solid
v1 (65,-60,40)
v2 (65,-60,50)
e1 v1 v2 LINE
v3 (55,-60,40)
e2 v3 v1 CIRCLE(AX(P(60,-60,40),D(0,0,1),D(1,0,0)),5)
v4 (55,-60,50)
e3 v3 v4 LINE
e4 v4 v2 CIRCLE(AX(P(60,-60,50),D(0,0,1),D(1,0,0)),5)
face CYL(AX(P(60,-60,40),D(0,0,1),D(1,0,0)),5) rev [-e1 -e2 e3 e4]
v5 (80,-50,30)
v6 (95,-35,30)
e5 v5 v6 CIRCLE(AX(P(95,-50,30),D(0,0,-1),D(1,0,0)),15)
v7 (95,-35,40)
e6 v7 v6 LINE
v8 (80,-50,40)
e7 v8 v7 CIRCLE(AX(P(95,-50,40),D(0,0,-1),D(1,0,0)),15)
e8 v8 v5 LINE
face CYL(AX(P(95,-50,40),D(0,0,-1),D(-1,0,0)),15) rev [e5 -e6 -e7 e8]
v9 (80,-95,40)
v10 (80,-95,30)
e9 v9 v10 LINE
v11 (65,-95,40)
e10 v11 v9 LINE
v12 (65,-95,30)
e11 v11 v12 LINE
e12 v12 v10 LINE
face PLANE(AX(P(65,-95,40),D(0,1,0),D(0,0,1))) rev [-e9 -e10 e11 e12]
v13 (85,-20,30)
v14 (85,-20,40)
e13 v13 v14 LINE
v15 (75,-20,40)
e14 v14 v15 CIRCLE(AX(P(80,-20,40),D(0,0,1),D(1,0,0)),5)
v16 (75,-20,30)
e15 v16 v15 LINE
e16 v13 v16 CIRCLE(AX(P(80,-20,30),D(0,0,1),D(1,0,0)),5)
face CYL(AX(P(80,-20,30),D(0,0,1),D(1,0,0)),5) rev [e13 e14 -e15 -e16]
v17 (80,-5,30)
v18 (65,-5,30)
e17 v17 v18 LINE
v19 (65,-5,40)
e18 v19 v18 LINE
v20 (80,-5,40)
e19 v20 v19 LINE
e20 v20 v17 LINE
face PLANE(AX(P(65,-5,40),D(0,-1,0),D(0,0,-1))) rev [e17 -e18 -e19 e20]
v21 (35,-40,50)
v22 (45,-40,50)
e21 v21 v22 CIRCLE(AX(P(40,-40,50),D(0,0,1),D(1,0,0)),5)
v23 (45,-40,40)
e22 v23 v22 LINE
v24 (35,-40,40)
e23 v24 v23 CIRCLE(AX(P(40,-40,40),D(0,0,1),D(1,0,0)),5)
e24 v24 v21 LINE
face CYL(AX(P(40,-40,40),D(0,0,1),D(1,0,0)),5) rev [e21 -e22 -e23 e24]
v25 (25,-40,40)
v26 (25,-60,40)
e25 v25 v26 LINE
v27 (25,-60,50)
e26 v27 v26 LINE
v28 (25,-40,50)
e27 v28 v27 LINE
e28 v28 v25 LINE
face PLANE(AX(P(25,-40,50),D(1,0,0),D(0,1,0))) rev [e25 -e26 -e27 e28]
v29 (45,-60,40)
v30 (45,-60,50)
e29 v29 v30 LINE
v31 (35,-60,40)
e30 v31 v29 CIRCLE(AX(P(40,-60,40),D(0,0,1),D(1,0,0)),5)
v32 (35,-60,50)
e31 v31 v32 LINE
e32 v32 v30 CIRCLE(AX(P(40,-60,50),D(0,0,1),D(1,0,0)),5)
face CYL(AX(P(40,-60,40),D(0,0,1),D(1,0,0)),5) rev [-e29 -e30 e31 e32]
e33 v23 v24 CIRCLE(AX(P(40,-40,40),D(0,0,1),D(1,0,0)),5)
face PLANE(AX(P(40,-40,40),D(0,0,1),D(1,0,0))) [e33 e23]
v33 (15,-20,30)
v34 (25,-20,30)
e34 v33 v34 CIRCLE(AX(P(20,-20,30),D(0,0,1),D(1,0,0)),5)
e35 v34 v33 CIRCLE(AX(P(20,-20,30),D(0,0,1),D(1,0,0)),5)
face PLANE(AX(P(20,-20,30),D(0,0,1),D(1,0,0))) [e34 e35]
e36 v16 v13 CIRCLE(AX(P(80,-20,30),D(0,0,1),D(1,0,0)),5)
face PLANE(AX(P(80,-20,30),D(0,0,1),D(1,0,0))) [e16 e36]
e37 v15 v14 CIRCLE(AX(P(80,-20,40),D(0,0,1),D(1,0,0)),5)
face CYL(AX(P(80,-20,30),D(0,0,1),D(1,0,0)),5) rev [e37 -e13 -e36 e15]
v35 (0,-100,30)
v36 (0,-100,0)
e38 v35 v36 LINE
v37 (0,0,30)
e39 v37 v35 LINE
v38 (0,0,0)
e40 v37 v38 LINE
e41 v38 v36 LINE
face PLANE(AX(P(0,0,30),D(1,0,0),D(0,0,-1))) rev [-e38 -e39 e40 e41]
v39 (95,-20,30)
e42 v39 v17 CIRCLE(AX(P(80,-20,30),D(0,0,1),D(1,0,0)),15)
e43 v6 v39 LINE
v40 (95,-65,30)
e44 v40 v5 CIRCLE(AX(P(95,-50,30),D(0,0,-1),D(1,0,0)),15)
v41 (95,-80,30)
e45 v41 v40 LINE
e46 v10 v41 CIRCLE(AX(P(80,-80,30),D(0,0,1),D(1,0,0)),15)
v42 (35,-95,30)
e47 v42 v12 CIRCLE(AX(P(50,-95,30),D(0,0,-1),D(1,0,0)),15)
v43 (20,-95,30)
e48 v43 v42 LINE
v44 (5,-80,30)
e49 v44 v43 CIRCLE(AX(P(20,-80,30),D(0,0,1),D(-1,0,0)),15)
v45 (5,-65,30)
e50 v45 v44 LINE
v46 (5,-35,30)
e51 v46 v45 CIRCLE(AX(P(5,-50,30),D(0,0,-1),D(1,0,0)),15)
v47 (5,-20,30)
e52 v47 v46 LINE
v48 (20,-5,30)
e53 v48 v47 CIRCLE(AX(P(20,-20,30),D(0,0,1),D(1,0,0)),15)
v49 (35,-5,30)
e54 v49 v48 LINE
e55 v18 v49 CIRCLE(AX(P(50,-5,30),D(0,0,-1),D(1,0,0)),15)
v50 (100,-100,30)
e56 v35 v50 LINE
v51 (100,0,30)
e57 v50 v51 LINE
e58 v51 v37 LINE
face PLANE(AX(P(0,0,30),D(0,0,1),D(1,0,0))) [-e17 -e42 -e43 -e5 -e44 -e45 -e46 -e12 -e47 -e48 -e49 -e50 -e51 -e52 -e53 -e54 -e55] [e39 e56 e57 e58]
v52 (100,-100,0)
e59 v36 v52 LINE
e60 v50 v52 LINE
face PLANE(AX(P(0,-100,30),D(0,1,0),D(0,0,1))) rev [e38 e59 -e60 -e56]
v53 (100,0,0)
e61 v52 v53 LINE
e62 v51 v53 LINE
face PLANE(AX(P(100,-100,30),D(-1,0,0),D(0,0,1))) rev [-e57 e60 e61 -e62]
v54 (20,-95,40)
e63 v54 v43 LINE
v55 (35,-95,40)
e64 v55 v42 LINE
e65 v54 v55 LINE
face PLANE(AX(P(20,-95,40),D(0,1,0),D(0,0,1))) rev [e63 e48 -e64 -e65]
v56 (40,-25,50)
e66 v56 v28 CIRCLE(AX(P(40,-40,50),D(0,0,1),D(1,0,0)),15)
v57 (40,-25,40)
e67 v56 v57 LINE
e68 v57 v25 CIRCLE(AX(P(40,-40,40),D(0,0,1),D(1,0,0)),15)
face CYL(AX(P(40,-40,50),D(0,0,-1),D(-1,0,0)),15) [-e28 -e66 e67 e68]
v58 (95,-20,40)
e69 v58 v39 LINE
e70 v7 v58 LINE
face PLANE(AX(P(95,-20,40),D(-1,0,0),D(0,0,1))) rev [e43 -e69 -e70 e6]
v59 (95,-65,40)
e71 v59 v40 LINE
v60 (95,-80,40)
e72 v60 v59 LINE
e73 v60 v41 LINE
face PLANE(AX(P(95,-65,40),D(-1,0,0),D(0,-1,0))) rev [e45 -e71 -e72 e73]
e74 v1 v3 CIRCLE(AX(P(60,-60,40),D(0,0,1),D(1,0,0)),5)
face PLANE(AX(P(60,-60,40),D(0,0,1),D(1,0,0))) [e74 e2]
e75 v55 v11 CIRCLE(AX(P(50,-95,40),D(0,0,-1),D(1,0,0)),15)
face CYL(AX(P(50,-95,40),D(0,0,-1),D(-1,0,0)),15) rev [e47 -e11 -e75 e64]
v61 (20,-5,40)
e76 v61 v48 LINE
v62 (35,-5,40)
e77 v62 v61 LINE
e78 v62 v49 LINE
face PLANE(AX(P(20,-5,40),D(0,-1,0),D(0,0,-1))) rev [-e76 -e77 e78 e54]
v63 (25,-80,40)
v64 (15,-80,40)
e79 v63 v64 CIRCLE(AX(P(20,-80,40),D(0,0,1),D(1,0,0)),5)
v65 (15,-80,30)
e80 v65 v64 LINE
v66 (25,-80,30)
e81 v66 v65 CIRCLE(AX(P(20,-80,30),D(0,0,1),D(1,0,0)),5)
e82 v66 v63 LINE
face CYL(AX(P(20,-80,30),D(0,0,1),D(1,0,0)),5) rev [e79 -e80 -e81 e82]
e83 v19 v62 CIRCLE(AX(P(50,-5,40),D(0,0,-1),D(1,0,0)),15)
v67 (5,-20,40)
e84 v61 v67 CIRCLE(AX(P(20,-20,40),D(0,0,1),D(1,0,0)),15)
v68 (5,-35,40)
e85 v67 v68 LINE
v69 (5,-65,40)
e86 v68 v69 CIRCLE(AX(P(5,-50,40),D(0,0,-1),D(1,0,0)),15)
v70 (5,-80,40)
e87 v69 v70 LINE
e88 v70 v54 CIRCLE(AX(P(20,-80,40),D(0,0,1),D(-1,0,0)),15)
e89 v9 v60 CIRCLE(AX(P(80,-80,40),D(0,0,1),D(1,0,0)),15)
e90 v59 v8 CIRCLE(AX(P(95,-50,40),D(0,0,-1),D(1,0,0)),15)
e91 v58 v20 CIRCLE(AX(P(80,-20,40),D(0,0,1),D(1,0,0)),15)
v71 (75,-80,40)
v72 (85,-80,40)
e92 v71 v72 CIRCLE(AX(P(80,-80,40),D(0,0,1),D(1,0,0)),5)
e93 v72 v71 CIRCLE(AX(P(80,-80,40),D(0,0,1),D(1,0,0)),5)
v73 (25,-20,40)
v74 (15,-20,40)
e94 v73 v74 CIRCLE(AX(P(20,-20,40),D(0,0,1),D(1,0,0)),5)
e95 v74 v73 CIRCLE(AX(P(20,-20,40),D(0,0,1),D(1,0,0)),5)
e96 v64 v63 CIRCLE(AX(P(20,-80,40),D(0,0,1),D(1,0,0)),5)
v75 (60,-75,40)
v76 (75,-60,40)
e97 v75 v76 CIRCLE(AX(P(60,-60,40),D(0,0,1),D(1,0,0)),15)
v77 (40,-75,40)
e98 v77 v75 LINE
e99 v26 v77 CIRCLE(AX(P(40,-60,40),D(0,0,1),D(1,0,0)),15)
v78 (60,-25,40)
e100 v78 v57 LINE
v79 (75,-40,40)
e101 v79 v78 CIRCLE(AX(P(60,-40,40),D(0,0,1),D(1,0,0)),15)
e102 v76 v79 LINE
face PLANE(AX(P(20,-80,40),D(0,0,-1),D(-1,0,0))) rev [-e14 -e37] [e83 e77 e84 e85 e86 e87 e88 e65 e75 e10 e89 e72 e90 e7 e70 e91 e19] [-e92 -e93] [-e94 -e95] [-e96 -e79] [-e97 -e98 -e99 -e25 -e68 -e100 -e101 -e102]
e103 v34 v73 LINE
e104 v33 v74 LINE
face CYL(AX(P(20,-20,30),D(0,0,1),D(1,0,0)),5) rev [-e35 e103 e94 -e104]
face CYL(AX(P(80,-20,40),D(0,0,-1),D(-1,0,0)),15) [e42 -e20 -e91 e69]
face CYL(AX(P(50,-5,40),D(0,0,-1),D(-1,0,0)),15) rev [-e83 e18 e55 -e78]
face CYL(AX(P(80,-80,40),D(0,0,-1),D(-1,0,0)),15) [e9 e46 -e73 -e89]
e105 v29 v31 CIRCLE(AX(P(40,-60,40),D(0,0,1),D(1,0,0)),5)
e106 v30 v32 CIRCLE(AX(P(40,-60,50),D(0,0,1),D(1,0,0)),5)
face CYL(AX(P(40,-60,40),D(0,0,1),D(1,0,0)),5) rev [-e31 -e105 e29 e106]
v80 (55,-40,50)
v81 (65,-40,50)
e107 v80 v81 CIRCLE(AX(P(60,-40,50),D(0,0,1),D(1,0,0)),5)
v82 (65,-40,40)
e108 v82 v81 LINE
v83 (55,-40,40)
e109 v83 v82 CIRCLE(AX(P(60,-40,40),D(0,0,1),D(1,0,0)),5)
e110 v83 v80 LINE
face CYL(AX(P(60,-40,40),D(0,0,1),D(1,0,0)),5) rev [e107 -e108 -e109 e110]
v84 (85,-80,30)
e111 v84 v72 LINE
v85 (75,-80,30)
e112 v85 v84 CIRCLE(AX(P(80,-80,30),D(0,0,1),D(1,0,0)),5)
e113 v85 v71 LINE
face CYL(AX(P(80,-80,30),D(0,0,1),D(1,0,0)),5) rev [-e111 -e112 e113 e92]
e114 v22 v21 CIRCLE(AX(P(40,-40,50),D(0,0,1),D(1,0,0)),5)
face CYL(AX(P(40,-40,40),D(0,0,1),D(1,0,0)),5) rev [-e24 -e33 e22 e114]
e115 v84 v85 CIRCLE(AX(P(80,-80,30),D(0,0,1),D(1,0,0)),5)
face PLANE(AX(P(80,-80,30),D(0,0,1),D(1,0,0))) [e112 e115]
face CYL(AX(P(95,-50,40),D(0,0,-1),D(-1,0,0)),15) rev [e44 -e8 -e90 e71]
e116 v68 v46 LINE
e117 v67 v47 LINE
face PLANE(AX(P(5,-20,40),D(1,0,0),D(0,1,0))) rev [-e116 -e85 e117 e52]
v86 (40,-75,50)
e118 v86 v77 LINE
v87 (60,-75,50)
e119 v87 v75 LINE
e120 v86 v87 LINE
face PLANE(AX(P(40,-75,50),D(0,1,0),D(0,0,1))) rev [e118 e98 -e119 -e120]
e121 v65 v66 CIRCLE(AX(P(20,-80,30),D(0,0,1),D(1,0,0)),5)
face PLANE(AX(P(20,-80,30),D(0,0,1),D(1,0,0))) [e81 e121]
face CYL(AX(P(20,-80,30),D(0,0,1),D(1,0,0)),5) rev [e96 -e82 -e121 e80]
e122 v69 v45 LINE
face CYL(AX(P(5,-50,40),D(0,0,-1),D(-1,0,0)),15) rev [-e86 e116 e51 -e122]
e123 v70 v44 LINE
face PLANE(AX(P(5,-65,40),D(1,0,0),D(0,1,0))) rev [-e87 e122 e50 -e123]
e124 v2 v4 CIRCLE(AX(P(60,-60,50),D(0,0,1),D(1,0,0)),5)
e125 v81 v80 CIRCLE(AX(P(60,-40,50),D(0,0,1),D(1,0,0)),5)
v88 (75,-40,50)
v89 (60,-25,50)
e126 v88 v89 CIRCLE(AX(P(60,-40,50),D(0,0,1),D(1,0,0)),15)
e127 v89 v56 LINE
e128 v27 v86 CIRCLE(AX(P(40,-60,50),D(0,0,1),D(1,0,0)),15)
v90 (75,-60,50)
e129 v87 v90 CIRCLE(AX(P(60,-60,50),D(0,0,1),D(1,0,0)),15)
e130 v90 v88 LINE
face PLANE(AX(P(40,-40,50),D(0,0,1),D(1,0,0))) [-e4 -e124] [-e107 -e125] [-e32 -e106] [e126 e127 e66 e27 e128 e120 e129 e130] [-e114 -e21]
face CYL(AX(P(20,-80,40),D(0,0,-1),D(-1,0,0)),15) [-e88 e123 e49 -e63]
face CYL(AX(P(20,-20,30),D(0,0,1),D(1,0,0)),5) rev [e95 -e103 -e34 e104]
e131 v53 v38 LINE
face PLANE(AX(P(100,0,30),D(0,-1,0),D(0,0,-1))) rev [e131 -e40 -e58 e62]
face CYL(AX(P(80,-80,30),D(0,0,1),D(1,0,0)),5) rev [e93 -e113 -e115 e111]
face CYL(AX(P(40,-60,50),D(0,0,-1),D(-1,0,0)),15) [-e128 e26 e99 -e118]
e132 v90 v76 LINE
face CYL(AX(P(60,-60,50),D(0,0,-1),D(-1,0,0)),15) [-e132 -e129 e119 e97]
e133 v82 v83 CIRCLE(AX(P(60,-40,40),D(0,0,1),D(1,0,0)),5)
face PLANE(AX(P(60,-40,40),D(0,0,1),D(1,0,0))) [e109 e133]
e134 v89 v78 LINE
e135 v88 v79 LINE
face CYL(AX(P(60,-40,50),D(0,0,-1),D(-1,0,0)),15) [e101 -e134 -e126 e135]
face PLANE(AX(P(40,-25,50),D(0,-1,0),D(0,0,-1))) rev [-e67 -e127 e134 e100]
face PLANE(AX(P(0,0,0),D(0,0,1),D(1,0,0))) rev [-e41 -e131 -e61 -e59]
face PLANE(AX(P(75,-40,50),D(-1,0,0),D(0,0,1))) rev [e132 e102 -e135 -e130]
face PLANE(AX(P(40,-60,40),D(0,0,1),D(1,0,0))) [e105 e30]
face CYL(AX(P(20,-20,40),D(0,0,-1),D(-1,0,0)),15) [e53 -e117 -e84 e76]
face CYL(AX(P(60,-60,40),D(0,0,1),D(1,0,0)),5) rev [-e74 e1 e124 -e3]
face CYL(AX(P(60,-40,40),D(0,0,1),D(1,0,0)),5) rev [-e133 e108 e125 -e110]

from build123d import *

# Parameters (mm, degrees)
BASE_BLOCK_SKETCH_W         = 100
BASE_BLOCK_SKETCH_H         = 100
BASE_BLOCK_100X100X30_DEPTH = 30
FLANGE_PLATE_DEPTH          = 10
CENTRE_BOSS_DEPTH           = 10
BOSS_HOLES_SKETCH_R         = 5
BOSS_HOLES_4X_10_DEPTH      = 10
FLANGE_HOLES_SKETCH_R       = 5
FLANGE_HOLES_4X_10_DEPTH    = 10


with BuildPart() as part:
    # Base Block Sketch → Base Block 100x100x30 (new body)
    with BuildSketch(Plane.XY):
        with Locations((50, -50)):
            Rectangle(BASE_BLOCK_SKETCH_W, BASE_BLOCK_SKETCH_H)
    extrude(amount=BASE_BLOCK_100X100X30_DEPTH)

    # Flange Plate Sketch → Flange Plate (add)
    with BuildSketch(Plane.XY.offset(30)):
        with BuildLine():
            Line((5, -65), (5, -80))
            ThreePointArc((5, -80), (9.393398282, -90.606601718), (20, -95))
            Line((20, -95), (35, -95))
            ThreePointArc((35, -95), (50, -80), (65, -95))
            Line((65, -95), (80, -95))
            ThreePointArc((80, -95), (90.606601718, -90.606601718), (95, -80))
            Line((95, -80), (95, -65))
            ThreePointArc((95, -65), (80, -50), (95, -35))
            Line((95, -35), (95, -20))
            ThreePointArc((95, -20), (90.606601718, -9.393398282), (80, -5))
            Line((80, -5), (65, -5))
            ThreePointArc((65, -5), (50, -20), (35, -5))
            Line((35, -5), (20, -5))
            ThreePointArc((20, -5), (9.393398282, -9.393398282), (5, -20))
            Line((5, -20), (5, -35))
            ThreePointArc((5, -35), (20, -50), (5, -65))
        make_face()
    extrude(amount=FLANGE_PLATE_DEPTH)

    # Centre Boss Sketch → Centre Boss (add)
    with BuildSketch(Plane.XY.offset(40)):
        with BuildLine():
            Line((25, -40), (25, -60))
            ThreePointArc((25, -60), (29.393398282, -70.606601718), (40, -75))
            Line((40, -75), (60, -75))
            ThreePointArc((60, -75), (70.606601718, -70.606601718), (75, -60))
            Line((75, -60), (75, -40))
            ThreePointArc((75, -40), (70.606601718, -29.393398282), (60, -25))
            Line((60, -25), (40, -25))
            ThreePointArc((40, -25), (29.393398282, -29.393398282), (25, -40))
        make_face()
    extrude(amount=CENTRE_BOSS_DEPTH)

    # Boss Holes Sketch → Boss Holes 4xØ10 (cut)
    with BuildSketch(Plane.XY.offset(50)):
        with Locations((40, -40)):
            Circle(BOSS_HOLES_SKETCH_R)
        with Locations((60, -40)):
            Circle(BOSS_HOLES_SKETCH_R)
        with Locations((60, -60)):
            Circle(BOSS_HOLES_SKETCH_R)
        with Locations((40, -60)):
            Circle(BOSS_HOLES_SKETCH_R)
    extrude(amount=-BOSS_HOLES_4X_10_DEPTH, mode=Mode.SUBTRACT)

    # Flange Holes Sketch → Flange Holes 4xØ10 (cut)
    with BuildSketch(Plane.XY.offset(40)):
        with Locations((20, -20)):
            Circle(FLANGE_HOLES_SKETCH_R)
        with Locations((80, -20)):
            Circle(FLANGE_HOLES_SKETCH_R)
        with Locations((80, -80)):
            Circle(FLANGE_HOLES_SKETCH_R)
        with Locations((20, -80)):
            Circle(FLANGE_HOLES_SKETCH_R)
    extrude(amount=-FLANGE_HOLES_4X_10_DEPTH, mode=Mode.SUBTRACT)


solid = part.part
